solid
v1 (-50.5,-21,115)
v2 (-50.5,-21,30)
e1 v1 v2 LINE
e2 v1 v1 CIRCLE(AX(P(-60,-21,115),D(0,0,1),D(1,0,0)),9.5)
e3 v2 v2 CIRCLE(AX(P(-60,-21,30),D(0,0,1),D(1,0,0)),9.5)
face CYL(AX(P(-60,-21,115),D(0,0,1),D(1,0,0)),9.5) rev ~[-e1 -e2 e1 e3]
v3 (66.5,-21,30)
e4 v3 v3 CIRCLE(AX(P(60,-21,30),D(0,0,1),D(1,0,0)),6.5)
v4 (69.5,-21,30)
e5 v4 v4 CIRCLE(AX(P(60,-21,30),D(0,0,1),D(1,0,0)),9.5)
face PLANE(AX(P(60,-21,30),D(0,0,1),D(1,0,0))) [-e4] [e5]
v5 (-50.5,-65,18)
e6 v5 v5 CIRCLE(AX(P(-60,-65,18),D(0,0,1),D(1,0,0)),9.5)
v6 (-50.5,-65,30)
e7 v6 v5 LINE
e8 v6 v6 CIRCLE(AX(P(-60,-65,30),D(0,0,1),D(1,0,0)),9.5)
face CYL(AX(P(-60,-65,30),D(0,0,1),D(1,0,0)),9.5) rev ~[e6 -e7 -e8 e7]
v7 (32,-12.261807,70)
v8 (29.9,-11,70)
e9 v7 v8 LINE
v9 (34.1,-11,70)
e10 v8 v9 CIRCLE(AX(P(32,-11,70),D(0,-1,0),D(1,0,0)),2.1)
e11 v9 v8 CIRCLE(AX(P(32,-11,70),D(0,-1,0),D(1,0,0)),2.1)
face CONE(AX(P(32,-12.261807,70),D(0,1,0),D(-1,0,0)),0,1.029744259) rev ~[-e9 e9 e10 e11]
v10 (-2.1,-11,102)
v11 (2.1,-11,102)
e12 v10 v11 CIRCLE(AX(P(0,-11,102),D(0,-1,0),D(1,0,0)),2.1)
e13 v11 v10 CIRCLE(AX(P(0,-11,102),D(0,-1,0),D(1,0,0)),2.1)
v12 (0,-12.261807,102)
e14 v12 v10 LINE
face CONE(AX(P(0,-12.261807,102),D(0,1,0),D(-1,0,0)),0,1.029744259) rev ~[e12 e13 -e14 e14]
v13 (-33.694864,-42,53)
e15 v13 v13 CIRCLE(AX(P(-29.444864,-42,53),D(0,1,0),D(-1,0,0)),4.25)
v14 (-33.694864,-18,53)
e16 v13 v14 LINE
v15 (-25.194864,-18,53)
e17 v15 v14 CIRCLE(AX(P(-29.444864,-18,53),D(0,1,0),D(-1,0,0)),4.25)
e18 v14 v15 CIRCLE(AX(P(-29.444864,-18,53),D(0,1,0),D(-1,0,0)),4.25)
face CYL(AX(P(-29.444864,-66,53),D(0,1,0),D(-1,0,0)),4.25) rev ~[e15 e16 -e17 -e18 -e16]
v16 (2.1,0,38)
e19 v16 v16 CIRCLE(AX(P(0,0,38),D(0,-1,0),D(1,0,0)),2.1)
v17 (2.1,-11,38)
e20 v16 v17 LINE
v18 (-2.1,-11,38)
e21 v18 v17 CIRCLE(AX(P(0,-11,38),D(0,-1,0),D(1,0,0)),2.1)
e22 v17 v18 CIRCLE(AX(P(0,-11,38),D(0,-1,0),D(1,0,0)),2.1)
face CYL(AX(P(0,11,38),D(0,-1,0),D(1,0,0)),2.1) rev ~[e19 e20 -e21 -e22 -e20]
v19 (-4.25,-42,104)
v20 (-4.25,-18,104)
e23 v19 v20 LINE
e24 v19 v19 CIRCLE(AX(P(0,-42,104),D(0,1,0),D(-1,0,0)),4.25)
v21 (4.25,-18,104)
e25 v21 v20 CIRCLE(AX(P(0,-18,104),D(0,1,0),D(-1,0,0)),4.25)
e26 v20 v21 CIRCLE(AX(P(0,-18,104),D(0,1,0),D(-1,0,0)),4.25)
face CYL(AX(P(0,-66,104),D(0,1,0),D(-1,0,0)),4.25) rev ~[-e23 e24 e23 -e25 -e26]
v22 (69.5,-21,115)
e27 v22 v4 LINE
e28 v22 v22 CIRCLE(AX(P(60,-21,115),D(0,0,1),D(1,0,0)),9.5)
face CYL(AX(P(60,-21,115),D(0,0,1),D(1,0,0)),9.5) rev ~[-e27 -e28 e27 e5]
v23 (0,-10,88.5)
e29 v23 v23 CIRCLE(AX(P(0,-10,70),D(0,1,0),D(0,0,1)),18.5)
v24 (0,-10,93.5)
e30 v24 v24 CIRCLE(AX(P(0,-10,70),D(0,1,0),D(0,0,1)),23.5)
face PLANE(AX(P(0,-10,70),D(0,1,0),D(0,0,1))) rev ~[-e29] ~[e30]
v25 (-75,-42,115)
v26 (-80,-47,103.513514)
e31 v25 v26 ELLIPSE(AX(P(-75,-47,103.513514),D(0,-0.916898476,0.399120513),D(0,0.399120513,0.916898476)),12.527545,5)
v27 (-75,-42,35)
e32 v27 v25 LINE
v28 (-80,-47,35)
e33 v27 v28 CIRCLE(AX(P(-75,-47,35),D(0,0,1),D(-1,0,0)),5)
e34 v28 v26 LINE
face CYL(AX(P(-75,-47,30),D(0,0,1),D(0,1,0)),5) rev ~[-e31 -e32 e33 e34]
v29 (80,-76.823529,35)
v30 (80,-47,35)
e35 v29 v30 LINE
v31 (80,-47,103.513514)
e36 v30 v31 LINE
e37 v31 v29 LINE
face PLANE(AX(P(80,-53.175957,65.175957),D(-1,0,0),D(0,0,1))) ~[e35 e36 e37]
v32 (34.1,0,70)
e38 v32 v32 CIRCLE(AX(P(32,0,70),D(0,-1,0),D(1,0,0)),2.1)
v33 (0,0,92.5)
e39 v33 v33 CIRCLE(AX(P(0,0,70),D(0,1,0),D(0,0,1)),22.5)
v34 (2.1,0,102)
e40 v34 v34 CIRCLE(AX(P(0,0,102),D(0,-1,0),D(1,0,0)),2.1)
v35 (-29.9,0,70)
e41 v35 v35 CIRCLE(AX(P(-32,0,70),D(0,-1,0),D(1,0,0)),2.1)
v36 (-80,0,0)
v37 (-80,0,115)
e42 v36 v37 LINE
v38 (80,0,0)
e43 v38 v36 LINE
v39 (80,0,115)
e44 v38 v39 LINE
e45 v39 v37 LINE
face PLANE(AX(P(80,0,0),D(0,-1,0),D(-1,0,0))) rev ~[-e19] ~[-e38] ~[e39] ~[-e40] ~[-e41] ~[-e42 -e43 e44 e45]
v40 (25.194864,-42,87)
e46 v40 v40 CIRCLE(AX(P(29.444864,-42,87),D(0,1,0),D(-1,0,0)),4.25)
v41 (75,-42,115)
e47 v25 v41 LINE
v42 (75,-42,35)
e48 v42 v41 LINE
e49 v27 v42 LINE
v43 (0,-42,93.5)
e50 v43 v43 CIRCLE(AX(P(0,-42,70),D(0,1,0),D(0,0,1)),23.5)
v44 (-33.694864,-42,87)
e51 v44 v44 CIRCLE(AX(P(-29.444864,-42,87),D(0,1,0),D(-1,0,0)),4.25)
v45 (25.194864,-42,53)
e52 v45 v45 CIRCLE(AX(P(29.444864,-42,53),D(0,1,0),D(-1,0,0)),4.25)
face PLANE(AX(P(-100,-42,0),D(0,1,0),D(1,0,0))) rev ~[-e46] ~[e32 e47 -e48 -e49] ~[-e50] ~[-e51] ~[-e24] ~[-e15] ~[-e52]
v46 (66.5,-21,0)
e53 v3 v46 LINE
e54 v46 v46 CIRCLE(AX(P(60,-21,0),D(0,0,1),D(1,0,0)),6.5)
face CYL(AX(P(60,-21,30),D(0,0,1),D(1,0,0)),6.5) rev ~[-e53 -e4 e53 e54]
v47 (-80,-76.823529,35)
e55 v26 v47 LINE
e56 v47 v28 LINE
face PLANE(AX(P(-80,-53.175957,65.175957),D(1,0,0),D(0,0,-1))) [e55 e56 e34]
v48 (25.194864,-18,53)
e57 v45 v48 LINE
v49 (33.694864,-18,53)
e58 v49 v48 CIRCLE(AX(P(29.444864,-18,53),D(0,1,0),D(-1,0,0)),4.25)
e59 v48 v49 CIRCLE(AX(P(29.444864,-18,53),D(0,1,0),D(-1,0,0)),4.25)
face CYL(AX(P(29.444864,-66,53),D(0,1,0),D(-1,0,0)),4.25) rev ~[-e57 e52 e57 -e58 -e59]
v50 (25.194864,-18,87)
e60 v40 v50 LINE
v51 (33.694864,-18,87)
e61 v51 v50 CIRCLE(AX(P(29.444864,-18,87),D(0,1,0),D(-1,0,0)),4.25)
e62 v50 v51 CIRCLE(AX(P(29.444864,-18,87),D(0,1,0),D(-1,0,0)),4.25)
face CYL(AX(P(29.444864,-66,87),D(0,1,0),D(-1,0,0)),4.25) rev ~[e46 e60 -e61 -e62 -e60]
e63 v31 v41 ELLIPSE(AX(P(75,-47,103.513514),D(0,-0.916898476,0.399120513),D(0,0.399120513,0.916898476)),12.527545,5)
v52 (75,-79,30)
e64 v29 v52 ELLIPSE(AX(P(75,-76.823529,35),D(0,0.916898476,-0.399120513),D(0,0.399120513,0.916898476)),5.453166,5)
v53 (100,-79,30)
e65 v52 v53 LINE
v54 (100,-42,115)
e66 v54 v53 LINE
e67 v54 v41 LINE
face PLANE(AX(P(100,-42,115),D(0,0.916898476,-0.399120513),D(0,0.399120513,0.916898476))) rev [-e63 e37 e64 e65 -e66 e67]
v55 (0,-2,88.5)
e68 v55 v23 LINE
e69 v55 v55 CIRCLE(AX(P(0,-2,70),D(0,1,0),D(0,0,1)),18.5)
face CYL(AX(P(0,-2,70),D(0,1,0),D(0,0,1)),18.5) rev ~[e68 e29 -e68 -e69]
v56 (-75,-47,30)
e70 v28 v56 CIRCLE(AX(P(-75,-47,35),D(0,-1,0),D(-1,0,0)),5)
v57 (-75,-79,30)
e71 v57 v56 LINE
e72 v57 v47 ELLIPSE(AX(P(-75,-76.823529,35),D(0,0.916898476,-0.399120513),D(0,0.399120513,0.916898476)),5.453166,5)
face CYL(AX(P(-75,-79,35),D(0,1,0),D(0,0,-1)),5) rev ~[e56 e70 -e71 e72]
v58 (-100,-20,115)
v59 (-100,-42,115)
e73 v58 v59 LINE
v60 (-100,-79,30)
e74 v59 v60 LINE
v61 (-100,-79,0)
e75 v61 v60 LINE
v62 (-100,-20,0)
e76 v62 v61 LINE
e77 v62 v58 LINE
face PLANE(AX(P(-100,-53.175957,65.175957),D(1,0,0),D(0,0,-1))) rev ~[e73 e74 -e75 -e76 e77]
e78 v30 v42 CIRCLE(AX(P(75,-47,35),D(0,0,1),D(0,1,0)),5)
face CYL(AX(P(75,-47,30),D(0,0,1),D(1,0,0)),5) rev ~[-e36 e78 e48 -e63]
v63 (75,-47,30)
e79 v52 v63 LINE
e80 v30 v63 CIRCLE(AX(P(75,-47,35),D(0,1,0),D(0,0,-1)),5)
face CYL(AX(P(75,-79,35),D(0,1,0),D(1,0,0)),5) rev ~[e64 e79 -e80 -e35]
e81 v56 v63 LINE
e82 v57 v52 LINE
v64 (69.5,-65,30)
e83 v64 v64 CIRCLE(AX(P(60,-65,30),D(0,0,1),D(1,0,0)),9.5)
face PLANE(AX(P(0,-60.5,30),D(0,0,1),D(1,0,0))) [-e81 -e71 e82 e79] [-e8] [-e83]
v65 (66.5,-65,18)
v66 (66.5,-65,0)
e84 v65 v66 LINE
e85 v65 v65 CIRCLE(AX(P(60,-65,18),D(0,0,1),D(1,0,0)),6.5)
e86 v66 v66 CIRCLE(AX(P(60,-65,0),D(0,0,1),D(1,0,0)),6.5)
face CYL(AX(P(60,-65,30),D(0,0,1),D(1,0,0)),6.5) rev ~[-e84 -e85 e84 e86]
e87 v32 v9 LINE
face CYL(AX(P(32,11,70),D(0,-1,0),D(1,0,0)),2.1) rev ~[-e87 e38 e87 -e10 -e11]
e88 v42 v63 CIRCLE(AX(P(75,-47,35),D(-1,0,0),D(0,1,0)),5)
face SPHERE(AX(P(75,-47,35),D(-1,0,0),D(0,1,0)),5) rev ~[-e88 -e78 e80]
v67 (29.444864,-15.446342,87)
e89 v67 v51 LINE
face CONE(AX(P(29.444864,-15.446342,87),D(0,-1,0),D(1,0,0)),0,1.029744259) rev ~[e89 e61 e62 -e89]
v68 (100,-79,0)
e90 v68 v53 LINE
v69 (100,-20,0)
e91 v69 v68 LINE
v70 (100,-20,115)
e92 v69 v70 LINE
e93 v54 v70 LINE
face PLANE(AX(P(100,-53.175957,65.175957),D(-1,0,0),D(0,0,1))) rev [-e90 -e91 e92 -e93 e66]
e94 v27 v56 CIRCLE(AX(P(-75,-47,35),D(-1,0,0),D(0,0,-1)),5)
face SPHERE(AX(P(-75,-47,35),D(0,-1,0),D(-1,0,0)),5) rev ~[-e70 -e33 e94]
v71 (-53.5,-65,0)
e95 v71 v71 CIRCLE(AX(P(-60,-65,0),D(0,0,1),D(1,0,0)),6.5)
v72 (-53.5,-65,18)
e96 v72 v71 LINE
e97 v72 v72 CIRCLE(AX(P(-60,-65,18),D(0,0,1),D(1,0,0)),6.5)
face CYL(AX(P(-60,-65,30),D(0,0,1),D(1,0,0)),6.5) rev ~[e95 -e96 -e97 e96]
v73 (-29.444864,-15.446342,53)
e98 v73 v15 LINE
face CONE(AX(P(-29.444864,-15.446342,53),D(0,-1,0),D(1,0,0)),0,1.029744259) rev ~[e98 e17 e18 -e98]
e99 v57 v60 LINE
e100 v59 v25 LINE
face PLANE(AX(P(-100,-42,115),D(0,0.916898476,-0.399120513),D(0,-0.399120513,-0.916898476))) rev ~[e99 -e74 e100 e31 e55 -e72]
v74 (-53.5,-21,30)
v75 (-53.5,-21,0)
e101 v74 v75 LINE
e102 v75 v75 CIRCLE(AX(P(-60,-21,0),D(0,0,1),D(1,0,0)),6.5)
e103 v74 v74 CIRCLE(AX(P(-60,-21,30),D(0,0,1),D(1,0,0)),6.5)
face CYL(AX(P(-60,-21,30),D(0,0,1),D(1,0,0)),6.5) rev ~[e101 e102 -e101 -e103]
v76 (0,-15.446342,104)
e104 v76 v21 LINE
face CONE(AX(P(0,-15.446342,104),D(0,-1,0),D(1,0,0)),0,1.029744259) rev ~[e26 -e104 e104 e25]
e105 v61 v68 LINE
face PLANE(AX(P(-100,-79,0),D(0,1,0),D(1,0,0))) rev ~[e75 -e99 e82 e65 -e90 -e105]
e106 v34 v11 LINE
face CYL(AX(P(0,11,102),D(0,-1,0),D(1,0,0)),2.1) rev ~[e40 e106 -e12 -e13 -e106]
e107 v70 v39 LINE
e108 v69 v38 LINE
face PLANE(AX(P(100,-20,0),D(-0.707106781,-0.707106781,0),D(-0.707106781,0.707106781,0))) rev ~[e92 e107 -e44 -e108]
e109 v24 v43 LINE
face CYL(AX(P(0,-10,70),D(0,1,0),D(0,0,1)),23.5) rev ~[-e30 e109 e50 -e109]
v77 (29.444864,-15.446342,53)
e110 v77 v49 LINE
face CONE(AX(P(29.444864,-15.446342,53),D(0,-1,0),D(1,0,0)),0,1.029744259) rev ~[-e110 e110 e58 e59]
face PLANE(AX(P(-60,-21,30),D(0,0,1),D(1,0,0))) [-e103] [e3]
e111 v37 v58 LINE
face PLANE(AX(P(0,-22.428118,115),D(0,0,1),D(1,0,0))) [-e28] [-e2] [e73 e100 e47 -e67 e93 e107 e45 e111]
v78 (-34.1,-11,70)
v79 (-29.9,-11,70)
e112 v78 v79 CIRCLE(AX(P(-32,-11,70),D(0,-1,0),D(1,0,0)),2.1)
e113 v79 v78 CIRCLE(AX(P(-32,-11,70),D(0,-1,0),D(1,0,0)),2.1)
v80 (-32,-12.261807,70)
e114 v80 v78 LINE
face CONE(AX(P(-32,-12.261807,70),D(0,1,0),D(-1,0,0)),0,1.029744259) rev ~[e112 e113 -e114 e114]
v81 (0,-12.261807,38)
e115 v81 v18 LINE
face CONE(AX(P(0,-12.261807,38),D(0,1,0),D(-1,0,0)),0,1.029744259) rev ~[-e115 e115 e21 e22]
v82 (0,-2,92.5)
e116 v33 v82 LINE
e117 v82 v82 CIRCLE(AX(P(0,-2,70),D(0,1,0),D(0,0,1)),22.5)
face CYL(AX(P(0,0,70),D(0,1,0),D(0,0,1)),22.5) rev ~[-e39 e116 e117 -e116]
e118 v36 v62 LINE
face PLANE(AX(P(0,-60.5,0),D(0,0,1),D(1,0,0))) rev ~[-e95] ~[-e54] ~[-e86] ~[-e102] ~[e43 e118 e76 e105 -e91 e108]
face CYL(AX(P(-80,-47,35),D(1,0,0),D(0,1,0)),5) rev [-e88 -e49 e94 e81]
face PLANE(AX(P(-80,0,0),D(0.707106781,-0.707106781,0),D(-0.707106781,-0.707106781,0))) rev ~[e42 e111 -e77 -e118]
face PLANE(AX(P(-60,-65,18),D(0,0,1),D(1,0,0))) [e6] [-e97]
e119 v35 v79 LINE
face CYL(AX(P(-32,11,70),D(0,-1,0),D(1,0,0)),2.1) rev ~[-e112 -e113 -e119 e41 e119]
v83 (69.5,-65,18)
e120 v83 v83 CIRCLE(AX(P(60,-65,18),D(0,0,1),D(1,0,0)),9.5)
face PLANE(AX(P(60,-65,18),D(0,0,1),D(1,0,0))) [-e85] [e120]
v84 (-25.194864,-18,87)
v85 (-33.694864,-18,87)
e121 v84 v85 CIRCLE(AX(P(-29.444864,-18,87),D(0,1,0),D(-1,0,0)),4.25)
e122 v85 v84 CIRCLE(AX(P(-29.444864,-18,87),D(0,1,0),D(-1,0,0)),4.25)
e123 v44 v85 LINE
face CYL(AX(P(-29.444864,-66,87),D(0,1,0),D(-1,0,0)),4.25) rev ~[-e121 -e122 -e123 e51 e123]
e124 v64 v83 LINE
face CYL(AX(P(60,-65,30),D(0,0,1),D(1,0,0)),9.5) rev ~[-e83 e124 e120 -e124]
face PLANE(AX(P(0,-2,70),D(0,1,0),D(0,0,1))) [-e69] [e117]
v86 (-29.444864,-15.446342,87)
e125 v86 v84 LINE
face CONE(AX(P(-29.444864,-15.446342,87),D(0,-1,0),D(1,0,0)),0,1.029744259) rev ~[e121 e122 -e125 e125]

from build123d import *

# Parameters (mm, degrees)
EXTRUDE_1_DEPTH         = 115
SKETCH_2_W              = 200
SKETCH_2_H              = 37
EXTRUDE_2_DEPTH         = 30
EXTRUDE_3_DEPTH         = 20
SKETCH_4_R              = 22.5
CUT_EXTRUDE_1_DEPTH     = 2
SKETCH_5_R              = 18.5
CUT_EXTRUDE_2_DEPTH     = 8
CUT_EXTRUDE_3_REACH     = 169.29
SKETCH_6_R              = 23.5
SKETCH_7_R              = 9.5
CUT_EXTRUDE_4_DEPTH     = 85
SKETCH_8_R              = 6.5
CUT_EXTRUDE_5_DEPTH     = 154.186161255
SKETCH_9_R              = 2.5
CUT_EXTRUDE_6_DEPTH     = 10
FILLET_1_R              = 5
SKETCH_10_R             = 1
CUT_EXTRUDE_7_DEPTH     = 5
M5X0_8_1_D              = 4.2
M5X0_8_1_DEPTH          = 11
M5X0_8_1_TIP            = 1.2618073
HOLE_WIZARD_M10_1_D     = 8.5
HOLE_WIZARD_M10_1_DEPTH = 24
HOLE_WIZARD_M10_1_TIP   = 2.553657631
SKETCH_15_R             = 6.5
CUT_EXTRUDE_8_DEPTH     = 55
SKETCH_16_R             = 9.5
CUT_EXTRUDE_9_DEPTH     = 12


with BuildPart() as part:
    # 草图1 → 拉伸1 (new body)
    with BuildSketch(Plane.XY):
        Polygon((80, 0), (-80, 0), (-100, -20), (-100, -42), (100, -42), (100, -20), align=None)
    extrude(amount=EXTRUDE_1_DEPTH)

    # 草图2 → 拉伸2 (add)
    with BuildSketch(Plane.XY):
        with Locations((0, -60.5)):
            Rectangle(SKETCH_2_W, SKETCH_2_H)
    extrude(amount=EXTRUDE_2_DEPTH)

    # 草图3 → 拉伸3 (add)
    with BuildSketch(Plane.ZY.offset(100)):
        Polygon((115, -42), (30, -79), (30, -42), align=None)
    extrude_3 = extrude(amount=-EXTRUDE_3_DEPTH)

    # 镜向1: 拉伸3 across plane
    add(extrude_3.mirror(Plane(origin=(0, 0, 0), x_dir=(0, 0, 1), z_dir=(1, 0, 0))))

    # 草图4 → 切除-拉伸1 (cut)
    with BuildSketch(Plane(origin=(0, 0, 0), x_dir=(1, 0, 0), z_dir=(0, 1, 0))):
        with Locations(Location((0, -70, 0), (0, 0, 270))):
            Circle(SKETCH_4_R)
    extrude(amount=-CUT_EXTRUDE_1_DEPTH, mode=Mode.SUBTRACT)

    # 草图5 → 切除-拉伸2 (cut)
    with BuildSketch(Plane(origin=(0, -2, 0), x_dir=(1, 0, 0), z_dir=(0, 1, 0))):
        with Locations(Location((0, -70, 0), (0, 0, 270))):
            Circle(SKETCH_5_R)
    extrude(amount=-CUT_EXTRUDE_2_DEPTH, mode=Mode.SUBTRACT)

    # 草图6 → 切除-拉伸3 (cut, up to next)
    with BuildSketch(Plane(origin=(0, -10, 0), x_dir=(1, 0, 0), z_dir=(0, 1, 0)), mode=Mode.PRIVATE) as cut_extrude_3_sk1:
        with Locations(Location((0, -70, 0), (0, 0, 270))):
            Circle(SKETCH_6_R)
    cut_extrude_3_tool1 = extrude(cut_extrude_3_sk1.sketch, amount=-CUT_EXTRUDE_3_REACH, mode=Mode.PRIVATE) & part.part
    add(cut_extrude_3_tool1.solids().sort_by_distance((0, -10, 70))[0], mode=Mode.SUBTRACT)

    # 草图7 → 切除-拉伸4 (cut)
    with BuildSketch(Plane.XY.offset(115)):
        with Locations((60, -21)):
            Circle(SKETCH_7_R)
        with Locations((-60, -21)):
            Circle(SKETCH_7_R)
    extrude(amount=-CUT_EXTRUDE_4_DEPTH, mode=Mode.SUBTRACT)

    # 草图8 → 切除-拉伸5 (cut, through all)
    with BuildSketch(Plane.XY.offset(30)):
        with Locations((-60, -21)):
            Circle(SKETCH_8_R)
        with Locations((60, -21)):
            Circle(SKETCH_8_R)
    extrude(amount=-CUT_EXTRUDE_5_DEPTH, mode=Mode.SUBTRACT)

    # 草图9 → 切除-拉伸6 (cut)
    with BuildSketch(Plane.XZ.offset(42)):
        with Locations(Location((0, 104, 0), (0, 0, 270))):
            Circle(SKETCH_9_R)
        with Locations(Location((29.444863729, 87, 0), (0, 0, 270))):
            Circle(SKETCH_9_R)
        with Locations(Location((29.444863729, 53, 0), (0, 0, 270))):
            Circle(SKETCH_9_R)
        with Locations(Location((-29.444863729, 87, 0), (0, 0, 270))):
            Circle(SKETCH_9_R)
        with Locations(Location((-29.444863729, 53, 0), (0, 0, 270))):
            Circle(SKETCH_9_R)
    extrude(amount=-CUT_EXTRUDE_6_DEPTH, mode=Mode.SUBTRACT)

    # 圆角1
    fillet_1_edges = [part.edges().sort_by_distance(p)[0] for p in [
        (-80, -60.5, 30),
        (-80, -42, 72.5),
        (0, -42, 30),
        (80, -42, 72.5),
        (80, -60.5, 30),
    ]]
    fillet(fillet_1_edges, radius=FILLET_1_R)

    # 草图10 → 切除-拉伸7 (cut)
    with BuildSketch(Plane(origin=(0, 0, 0), x_dir=(1, 0, 0), z_dir=(0, 1, 0))):
        with Locations(Location((0, -38, 0), (0, 0, 270))):
            Circle(SKETCH_10_R)
        with Locations(Location((32, -70, 0), (0, 0, 270))):
            Circle(SKETCH_10_R)
        with Locations(Location((0, -102, 0), (0, 0, 270))):
            Circle(SKETCH_10_R)
        with Locations(Location((-32, -70, 0), (0, 0, 270))):
            Circle(SKETCH_10_R)
    extrude(amount=-CUT_EXTRUDE_7_DEPTH, mode=Mode.SUBTRACT)

    # M5x0.8 螺纹孔1
    with Locations(Plane(origin=(0, 0, 0), x_dir=(-1, 0, 0), z_dir=(0, 1, 0))):
        with Locations((0, 38), (-32, 70), (0, 102), (32, 70)):
            Hole(M5X0_8_1_D / 2, depth=M5X0_8_1_DEPTH)
            with Locations((0, 0, -(M5X0_8_1_DEPTH + M5X0_8_1_TIP / 2))):  # 118° drill point
                Cone(0, M5X0_8_1_D / 2, M5X0_8_1_TIP, mode=Mode.SUBTRACT)

    # M10 螺纹孔1
    with Locations(Plane.XZ.offset(42)):
        with Locations((29.444863729, 53), (29.444863729, 87), (0, 104), (-29.444863729, 87), (-29.444863729, 53)):
            Hole(HOLE_WIZARD_M10_1_D / 2, depth=HOLE_WIZARD_M10_1_DEPTH)
            with Locations((0, 0, -(HOLE_WIZARD_M10_1_DEPTH + HOLE_WIZARD_M10_1_TIP / 2))):  # 118° drill point
                Cone(0, HOLE_WIZARD_M10_1_D / 2, HOLE_WIZARD_M10_1_TIP, mode=Mode.SUBTRACT)

    # 草图15 → 切除-拉伸8 (cut)
    with BuildSketch(Plane.XY.offset(30)):
        with Locations((-60, -65)):
            Circle(SKETCH_15_R)
        with Locations((60, -65)):
            Circle(SKETCH_15_R)
    extrude(amount=-CUT_EXTRUDE_8_DEPTH, mode=Mode.SUBTRACT)

    # 草图16 → 切除-拉伸9 (cut)
    with BuildSketch(Plane.XY.offset(30)):
        with Locations((-60, -65)):
            Circle(SKETCH_16_R)
        with Locations((60, -65)):
            Circle(SKETCH_16_R)
    extrude(amount=-CUT_EXTRUDE_9_DEPTH, mode=Mode.SUBTRACT)


solid = part.part
